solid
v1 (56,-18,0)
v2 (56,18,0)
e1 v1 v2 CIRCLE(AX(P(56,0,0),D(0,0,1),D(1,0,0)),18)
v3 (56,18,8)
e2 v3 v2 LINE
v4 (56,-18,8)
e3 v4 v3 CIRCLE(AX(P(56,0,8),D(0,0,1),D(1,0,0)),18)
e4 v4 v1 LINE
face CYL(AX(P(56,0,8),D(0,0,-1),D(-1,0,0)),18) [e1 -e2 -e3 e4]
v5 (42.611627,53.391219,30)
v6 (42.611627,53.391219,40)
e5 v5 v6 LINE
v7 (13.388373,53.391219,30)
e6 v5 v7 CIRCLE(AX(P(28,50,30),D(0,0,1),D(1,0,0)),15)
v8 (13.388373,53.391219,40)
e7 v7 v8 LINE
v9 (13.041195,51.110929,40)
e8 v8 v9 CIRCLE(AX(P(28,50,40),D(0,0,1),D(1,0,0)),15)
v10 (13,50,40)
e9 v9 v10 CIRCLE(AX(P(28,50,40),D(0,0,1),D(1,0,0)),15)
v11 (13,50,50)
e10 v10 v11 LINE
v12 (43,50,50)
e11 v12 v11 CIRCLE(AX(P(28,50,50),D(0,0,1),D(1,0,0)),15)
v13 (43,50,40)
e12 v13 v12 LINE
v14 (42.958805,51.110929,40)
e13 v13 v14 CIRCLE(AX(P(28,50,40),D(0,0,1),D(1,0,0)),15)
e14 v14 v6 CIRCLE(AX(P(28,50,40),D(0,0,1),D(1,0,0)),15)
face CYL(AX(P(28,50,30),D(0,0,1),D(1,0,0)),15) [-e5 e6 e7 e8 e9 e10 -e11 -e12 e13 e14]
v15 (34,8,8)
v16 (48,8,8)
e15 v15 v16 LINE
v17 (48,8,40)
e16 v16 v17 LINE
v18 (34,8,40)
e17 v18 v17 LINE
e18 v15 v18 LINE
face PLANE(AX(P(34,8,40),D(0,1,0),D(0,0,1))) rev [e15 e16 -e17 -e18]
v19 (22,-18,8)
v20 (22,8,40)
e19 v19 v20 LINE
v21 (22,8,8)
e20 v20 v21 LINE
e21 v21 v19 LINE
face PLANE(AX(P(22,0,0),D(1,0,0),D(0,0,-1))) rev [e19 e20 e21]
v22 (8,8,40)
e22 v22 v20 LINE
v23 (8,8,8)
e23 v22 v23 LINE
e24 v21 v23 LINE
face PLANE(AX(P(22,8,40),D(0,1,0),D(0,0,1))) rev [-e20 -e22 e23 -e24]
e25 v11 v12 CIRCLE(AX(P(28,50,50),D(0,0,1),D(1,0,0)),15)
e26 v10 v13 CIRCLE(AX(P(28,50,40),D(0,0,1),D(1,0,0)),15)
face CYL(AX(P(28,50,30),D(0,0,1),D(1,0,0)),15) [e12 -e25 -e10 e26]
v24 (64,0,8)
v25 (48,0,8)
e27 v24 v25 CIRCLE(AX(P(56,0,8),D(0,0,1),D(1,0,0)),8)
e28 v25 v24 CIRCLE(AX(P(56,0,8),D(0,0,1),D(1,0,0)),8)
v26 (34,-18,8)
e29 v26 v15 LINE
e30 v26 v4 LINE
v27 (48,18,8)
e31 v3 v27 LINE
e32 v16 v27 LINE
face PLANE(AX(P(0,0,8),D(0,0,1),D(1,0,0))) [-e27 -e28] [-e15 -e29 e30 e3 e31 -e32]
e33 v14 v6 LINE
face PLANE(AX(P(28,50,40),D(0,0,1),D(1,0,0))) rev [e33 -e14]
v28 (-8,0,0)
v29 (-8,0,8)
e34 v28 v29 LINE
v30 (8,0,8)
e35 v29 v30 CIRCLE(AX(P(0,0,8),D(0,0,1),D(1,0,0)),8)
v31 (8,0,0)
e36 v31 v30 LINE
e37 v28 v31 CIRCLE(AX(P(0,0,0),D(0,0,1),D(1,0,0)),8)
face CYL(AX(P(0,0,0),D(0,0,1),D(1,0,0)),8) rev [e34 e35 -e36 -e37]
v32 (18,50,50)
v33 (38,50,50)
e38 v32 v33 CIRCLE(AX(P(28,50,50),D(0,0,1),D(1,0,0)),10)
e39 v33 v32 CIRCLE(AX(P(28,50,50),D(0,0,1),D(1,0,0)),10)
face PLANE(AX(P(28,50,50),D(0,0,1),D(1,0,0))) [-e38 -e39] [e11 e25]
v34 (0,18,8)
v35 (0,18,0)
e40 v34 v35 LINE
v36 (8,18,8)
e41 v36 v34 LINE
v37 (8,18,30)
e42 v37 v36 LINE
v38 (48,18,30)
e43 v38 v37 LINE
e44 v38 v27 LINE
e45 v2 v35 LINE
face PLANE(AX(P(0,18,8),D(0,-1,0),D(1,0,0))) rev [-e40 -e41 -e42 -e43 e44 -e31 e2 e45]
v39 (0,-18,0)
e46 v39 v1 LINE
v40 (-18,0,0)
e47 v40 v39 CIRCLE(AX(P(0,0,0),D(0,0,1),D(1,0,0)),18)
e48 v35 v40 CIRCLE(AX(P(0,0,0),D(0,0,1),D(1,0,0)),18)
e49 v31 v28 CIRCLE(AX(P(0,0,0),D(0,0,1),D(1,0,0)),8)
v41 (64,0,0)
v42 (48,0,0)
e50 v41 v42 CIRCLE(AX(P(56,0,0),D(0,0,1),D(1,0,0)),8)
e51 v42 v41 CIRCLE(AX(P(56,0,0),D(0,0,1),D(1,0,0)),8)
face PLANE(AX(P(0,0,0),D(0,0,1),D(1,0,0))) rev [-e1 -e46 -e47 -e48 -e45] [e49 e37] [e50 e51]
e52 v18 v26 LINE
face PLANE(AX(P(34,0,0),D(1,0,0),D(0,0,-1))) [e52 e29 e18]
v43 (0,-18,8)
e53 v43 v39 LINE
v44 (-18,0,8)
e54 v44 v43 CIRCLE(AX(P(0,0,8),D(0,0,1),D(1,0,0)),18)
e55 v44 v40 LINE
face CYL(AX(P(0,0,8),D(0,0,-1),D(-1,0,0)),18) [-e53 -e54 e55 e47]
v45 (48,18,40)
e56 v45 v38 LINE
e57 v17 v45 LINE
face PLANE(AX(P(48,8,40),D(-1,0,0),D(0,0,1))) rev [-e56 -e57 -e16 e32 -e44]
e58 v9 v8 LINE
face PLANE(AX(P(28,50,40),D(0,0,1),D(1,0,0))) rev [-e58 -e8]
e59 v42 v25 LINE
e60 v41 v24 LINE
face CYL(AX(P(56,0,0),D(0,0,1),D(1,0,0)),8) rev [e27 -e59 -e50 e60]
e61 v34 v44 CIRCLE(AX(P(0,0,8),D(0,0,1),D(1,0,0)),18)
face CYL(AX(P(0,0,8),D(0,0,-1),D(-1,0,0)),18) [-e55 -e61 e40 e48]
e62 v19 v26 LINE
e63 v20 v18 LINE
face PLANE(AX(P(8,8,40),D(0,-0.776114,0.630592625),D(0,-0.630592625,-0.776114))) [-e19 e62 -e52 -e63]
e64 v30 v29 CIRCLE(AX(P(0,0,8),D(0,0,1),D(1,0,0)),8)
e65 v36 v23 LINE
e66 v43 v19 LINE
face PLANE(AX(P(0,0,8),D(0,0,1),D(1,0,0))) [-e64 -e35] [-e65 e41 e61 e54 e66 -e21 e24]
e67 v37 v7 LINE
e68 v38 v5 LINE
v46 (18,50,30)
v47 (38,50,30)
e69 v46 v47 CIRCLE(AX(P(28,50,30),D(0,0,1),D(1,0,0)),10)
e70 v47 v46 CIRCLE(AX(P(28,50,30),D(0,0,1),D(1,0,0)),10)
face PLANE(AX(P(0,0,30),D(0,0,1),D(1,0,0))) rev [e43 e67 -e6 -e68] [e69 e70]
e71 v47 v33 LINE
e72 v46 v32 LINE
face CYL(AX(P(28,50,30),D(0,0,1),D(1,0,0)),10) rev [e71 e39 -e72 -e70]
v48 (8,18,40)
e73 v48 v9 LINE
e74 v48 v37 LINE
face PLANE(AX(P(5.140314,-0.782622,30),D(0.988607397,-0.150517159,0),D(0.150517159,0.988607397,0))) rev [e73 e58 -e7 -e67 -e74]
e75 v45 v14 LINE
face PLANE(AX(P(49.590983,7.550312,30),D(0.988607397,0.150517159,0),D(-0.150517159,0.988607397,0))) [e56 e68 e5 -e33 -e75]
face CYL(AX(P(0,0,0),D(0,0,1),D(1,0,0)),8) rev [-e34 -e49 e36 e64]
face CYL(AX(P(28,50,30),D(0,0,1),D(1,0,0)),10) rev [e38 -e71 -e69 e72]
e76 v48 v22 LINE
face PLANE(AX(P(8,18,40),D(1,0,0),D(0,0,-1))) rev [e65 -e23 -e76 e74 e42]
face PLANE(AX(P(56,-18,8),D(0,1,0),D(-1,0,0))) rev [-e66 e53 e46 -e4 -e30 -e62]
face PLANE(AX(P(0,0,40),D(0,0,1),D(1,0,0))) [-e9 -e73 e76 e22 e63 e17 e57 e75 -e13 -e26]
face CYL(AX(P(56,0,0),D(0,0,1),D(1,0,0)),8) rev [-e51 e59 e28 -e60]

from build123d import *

# Parameters (mm, degrees)
BASE_PLATE_DEPTH       = 8
BASE_HOLE_SKETCH_R     = 8
BASE_HOLE_DEPTH        = 8
UPRIGHT_ARM_DEPTH      = 32
BOSS_MOUNT_DEPTH       = 10
CYLINDER_START         = 10
CYLINDER_BOSS_SKETCH_R = 15
CYLINDER_BOSS_DEPTH    = 10
BOSS_BORE_SKETCH_R     = 10
BOSS_BORE_DEPTH        = 20
GUSSET_DEPTH           = 40
GUSSET_TRIM_1_DEPTH    = 14
GUSSET_TRIM_2_DEPTH    = 14


with BuildPart() as part:
    # Base Plate Sketch → Base Plate (new body)
    with BuildSketch(Plane.XY):
        with BuildLine():
            Line((0, 18), (56, 18))
            ThreePointArc((56, 18), (74, 0), (56, -18))
            Line((56, -18), (0, -18))
            ThreePointArc((0, -18), (-18, 0), (0, 18))
        make_face()
    extrude(amount=BASE_PLATE_DEPTH)

    # Base Hole Sketch → Base Hole (cut)
    with BuildSketch(Plane.XY.offset(8)):
        Circle(BASE_HOLE_SKETCH_R)
        with Locations((56, 0)):
            Circle(BASE_HOLE_SKETCH_R)
    extrude(amount=-BASE_HOLE_DEPTH, mode=Mode.SUBTRACT)

    # Upright Arm Sketch → Upright Arm (add)
    with BuildSketch(Plane.XY.offset(8)):
        Polygon((28, 18), (8, 18), (8, 8), (48, 8), (48, 18), align=None)
    extrude(amount=UPRIGHT_ARM_DEPTH)

    # Boss Mount Sketch → Boss Mount (add)
    with BuildSketch(Plane.XY.offset(40)):
        with BuildLine():
            Line((13.388373349, 53.391219044), (13.041195377, 51.110929457))
            ThreePointArc((13.041195377, 51.110929457), (27.444153502, 35.010302382), (43, 50))
            ThreePointArc((43, 50), (42.989697618, 50.555846498), (42.958804623, 51.110929457))
            Line((42.958804623, 51.110929457), (42.611626651, 53.391219044))
            ThreePointArc((42.611626651, 53.391219044), (28, 65), (13.388373349, 53.391219044))
        make_face()
        with BuildLine():
            Line((13.041195377, 51.110929457), (8, 18))
            Line((8, 18), (48, 18))
            Line((48, 18), (42.958804623, 51.110929457))
            ThreePointArc((42.958804623, 51.110929457), (42.989697618, 50.555846498), (43, 50))
            ThreePointArc((43, 50), (27.444153502, 35.010302382), (13.041195377, 51.110929457))
        make_face()
    extrude(amount=-BOSS_MOUNT_DEPTH)

    # Cylinder Boss Sketch → Cylinder Boss (add)
    with BuildSketch(Plane.XY.offset(40).offset(CYLINDER_START)):
        with Locations((28, 50)):
            Circle(CYLINDER_BOSS_SKETCH_R)
    extrude(amount=-CYLINDER_BOSS_DEPTH)

    # Boss Bore Sketch → Boss Bore (cut)
    with BuildSketch(Plane.XY.offset(50)):
        with Locations((28, 50)):
            Circle(BOSS_BORE_SKETCH_R)
    extrude(amount=-BOSS_BORE_DEPTH, mode=Mode.SUBTRACT)

    # Gusset Sketch → Gusset (add)
    with BuildSketch(Plane(origin=(48, 0, 0), x_dir=(0, 0, -1), z_dir=(1, 0, 0))):
        Polygon((-40, 8), (-8, -18), (-8, 8), align=None)
    extrude(amount=-GUSSET_DEPTH)

    # Gusset Trim 1 Sketch → Gusset Trim 1 (cut)
    with BuildSketch(Plane(origin=(48, 0, 0), x_dir=(0, 0, -1), z_dir=(1, 0, 0))):
        Polygon((-40, 8), (-8, 8), (-8, -18), align=None)
    extrude(amount=-GUSSET_TRIM_1_DEPTH, mode=Mode.SUBTRACT)

    # Gusset Trim 2 Sketch → Gusset Trim 2 (cut)
    with BuildSketch(Plane.ZY.offset(-8)):
        Polygon((40, 8), (8, 8), (8, -18), align=None)
    extrude(amount=-GUSSET_TRIM_2_DEPTH, mode=Mode.SUBTRACT)


solid = part.part
